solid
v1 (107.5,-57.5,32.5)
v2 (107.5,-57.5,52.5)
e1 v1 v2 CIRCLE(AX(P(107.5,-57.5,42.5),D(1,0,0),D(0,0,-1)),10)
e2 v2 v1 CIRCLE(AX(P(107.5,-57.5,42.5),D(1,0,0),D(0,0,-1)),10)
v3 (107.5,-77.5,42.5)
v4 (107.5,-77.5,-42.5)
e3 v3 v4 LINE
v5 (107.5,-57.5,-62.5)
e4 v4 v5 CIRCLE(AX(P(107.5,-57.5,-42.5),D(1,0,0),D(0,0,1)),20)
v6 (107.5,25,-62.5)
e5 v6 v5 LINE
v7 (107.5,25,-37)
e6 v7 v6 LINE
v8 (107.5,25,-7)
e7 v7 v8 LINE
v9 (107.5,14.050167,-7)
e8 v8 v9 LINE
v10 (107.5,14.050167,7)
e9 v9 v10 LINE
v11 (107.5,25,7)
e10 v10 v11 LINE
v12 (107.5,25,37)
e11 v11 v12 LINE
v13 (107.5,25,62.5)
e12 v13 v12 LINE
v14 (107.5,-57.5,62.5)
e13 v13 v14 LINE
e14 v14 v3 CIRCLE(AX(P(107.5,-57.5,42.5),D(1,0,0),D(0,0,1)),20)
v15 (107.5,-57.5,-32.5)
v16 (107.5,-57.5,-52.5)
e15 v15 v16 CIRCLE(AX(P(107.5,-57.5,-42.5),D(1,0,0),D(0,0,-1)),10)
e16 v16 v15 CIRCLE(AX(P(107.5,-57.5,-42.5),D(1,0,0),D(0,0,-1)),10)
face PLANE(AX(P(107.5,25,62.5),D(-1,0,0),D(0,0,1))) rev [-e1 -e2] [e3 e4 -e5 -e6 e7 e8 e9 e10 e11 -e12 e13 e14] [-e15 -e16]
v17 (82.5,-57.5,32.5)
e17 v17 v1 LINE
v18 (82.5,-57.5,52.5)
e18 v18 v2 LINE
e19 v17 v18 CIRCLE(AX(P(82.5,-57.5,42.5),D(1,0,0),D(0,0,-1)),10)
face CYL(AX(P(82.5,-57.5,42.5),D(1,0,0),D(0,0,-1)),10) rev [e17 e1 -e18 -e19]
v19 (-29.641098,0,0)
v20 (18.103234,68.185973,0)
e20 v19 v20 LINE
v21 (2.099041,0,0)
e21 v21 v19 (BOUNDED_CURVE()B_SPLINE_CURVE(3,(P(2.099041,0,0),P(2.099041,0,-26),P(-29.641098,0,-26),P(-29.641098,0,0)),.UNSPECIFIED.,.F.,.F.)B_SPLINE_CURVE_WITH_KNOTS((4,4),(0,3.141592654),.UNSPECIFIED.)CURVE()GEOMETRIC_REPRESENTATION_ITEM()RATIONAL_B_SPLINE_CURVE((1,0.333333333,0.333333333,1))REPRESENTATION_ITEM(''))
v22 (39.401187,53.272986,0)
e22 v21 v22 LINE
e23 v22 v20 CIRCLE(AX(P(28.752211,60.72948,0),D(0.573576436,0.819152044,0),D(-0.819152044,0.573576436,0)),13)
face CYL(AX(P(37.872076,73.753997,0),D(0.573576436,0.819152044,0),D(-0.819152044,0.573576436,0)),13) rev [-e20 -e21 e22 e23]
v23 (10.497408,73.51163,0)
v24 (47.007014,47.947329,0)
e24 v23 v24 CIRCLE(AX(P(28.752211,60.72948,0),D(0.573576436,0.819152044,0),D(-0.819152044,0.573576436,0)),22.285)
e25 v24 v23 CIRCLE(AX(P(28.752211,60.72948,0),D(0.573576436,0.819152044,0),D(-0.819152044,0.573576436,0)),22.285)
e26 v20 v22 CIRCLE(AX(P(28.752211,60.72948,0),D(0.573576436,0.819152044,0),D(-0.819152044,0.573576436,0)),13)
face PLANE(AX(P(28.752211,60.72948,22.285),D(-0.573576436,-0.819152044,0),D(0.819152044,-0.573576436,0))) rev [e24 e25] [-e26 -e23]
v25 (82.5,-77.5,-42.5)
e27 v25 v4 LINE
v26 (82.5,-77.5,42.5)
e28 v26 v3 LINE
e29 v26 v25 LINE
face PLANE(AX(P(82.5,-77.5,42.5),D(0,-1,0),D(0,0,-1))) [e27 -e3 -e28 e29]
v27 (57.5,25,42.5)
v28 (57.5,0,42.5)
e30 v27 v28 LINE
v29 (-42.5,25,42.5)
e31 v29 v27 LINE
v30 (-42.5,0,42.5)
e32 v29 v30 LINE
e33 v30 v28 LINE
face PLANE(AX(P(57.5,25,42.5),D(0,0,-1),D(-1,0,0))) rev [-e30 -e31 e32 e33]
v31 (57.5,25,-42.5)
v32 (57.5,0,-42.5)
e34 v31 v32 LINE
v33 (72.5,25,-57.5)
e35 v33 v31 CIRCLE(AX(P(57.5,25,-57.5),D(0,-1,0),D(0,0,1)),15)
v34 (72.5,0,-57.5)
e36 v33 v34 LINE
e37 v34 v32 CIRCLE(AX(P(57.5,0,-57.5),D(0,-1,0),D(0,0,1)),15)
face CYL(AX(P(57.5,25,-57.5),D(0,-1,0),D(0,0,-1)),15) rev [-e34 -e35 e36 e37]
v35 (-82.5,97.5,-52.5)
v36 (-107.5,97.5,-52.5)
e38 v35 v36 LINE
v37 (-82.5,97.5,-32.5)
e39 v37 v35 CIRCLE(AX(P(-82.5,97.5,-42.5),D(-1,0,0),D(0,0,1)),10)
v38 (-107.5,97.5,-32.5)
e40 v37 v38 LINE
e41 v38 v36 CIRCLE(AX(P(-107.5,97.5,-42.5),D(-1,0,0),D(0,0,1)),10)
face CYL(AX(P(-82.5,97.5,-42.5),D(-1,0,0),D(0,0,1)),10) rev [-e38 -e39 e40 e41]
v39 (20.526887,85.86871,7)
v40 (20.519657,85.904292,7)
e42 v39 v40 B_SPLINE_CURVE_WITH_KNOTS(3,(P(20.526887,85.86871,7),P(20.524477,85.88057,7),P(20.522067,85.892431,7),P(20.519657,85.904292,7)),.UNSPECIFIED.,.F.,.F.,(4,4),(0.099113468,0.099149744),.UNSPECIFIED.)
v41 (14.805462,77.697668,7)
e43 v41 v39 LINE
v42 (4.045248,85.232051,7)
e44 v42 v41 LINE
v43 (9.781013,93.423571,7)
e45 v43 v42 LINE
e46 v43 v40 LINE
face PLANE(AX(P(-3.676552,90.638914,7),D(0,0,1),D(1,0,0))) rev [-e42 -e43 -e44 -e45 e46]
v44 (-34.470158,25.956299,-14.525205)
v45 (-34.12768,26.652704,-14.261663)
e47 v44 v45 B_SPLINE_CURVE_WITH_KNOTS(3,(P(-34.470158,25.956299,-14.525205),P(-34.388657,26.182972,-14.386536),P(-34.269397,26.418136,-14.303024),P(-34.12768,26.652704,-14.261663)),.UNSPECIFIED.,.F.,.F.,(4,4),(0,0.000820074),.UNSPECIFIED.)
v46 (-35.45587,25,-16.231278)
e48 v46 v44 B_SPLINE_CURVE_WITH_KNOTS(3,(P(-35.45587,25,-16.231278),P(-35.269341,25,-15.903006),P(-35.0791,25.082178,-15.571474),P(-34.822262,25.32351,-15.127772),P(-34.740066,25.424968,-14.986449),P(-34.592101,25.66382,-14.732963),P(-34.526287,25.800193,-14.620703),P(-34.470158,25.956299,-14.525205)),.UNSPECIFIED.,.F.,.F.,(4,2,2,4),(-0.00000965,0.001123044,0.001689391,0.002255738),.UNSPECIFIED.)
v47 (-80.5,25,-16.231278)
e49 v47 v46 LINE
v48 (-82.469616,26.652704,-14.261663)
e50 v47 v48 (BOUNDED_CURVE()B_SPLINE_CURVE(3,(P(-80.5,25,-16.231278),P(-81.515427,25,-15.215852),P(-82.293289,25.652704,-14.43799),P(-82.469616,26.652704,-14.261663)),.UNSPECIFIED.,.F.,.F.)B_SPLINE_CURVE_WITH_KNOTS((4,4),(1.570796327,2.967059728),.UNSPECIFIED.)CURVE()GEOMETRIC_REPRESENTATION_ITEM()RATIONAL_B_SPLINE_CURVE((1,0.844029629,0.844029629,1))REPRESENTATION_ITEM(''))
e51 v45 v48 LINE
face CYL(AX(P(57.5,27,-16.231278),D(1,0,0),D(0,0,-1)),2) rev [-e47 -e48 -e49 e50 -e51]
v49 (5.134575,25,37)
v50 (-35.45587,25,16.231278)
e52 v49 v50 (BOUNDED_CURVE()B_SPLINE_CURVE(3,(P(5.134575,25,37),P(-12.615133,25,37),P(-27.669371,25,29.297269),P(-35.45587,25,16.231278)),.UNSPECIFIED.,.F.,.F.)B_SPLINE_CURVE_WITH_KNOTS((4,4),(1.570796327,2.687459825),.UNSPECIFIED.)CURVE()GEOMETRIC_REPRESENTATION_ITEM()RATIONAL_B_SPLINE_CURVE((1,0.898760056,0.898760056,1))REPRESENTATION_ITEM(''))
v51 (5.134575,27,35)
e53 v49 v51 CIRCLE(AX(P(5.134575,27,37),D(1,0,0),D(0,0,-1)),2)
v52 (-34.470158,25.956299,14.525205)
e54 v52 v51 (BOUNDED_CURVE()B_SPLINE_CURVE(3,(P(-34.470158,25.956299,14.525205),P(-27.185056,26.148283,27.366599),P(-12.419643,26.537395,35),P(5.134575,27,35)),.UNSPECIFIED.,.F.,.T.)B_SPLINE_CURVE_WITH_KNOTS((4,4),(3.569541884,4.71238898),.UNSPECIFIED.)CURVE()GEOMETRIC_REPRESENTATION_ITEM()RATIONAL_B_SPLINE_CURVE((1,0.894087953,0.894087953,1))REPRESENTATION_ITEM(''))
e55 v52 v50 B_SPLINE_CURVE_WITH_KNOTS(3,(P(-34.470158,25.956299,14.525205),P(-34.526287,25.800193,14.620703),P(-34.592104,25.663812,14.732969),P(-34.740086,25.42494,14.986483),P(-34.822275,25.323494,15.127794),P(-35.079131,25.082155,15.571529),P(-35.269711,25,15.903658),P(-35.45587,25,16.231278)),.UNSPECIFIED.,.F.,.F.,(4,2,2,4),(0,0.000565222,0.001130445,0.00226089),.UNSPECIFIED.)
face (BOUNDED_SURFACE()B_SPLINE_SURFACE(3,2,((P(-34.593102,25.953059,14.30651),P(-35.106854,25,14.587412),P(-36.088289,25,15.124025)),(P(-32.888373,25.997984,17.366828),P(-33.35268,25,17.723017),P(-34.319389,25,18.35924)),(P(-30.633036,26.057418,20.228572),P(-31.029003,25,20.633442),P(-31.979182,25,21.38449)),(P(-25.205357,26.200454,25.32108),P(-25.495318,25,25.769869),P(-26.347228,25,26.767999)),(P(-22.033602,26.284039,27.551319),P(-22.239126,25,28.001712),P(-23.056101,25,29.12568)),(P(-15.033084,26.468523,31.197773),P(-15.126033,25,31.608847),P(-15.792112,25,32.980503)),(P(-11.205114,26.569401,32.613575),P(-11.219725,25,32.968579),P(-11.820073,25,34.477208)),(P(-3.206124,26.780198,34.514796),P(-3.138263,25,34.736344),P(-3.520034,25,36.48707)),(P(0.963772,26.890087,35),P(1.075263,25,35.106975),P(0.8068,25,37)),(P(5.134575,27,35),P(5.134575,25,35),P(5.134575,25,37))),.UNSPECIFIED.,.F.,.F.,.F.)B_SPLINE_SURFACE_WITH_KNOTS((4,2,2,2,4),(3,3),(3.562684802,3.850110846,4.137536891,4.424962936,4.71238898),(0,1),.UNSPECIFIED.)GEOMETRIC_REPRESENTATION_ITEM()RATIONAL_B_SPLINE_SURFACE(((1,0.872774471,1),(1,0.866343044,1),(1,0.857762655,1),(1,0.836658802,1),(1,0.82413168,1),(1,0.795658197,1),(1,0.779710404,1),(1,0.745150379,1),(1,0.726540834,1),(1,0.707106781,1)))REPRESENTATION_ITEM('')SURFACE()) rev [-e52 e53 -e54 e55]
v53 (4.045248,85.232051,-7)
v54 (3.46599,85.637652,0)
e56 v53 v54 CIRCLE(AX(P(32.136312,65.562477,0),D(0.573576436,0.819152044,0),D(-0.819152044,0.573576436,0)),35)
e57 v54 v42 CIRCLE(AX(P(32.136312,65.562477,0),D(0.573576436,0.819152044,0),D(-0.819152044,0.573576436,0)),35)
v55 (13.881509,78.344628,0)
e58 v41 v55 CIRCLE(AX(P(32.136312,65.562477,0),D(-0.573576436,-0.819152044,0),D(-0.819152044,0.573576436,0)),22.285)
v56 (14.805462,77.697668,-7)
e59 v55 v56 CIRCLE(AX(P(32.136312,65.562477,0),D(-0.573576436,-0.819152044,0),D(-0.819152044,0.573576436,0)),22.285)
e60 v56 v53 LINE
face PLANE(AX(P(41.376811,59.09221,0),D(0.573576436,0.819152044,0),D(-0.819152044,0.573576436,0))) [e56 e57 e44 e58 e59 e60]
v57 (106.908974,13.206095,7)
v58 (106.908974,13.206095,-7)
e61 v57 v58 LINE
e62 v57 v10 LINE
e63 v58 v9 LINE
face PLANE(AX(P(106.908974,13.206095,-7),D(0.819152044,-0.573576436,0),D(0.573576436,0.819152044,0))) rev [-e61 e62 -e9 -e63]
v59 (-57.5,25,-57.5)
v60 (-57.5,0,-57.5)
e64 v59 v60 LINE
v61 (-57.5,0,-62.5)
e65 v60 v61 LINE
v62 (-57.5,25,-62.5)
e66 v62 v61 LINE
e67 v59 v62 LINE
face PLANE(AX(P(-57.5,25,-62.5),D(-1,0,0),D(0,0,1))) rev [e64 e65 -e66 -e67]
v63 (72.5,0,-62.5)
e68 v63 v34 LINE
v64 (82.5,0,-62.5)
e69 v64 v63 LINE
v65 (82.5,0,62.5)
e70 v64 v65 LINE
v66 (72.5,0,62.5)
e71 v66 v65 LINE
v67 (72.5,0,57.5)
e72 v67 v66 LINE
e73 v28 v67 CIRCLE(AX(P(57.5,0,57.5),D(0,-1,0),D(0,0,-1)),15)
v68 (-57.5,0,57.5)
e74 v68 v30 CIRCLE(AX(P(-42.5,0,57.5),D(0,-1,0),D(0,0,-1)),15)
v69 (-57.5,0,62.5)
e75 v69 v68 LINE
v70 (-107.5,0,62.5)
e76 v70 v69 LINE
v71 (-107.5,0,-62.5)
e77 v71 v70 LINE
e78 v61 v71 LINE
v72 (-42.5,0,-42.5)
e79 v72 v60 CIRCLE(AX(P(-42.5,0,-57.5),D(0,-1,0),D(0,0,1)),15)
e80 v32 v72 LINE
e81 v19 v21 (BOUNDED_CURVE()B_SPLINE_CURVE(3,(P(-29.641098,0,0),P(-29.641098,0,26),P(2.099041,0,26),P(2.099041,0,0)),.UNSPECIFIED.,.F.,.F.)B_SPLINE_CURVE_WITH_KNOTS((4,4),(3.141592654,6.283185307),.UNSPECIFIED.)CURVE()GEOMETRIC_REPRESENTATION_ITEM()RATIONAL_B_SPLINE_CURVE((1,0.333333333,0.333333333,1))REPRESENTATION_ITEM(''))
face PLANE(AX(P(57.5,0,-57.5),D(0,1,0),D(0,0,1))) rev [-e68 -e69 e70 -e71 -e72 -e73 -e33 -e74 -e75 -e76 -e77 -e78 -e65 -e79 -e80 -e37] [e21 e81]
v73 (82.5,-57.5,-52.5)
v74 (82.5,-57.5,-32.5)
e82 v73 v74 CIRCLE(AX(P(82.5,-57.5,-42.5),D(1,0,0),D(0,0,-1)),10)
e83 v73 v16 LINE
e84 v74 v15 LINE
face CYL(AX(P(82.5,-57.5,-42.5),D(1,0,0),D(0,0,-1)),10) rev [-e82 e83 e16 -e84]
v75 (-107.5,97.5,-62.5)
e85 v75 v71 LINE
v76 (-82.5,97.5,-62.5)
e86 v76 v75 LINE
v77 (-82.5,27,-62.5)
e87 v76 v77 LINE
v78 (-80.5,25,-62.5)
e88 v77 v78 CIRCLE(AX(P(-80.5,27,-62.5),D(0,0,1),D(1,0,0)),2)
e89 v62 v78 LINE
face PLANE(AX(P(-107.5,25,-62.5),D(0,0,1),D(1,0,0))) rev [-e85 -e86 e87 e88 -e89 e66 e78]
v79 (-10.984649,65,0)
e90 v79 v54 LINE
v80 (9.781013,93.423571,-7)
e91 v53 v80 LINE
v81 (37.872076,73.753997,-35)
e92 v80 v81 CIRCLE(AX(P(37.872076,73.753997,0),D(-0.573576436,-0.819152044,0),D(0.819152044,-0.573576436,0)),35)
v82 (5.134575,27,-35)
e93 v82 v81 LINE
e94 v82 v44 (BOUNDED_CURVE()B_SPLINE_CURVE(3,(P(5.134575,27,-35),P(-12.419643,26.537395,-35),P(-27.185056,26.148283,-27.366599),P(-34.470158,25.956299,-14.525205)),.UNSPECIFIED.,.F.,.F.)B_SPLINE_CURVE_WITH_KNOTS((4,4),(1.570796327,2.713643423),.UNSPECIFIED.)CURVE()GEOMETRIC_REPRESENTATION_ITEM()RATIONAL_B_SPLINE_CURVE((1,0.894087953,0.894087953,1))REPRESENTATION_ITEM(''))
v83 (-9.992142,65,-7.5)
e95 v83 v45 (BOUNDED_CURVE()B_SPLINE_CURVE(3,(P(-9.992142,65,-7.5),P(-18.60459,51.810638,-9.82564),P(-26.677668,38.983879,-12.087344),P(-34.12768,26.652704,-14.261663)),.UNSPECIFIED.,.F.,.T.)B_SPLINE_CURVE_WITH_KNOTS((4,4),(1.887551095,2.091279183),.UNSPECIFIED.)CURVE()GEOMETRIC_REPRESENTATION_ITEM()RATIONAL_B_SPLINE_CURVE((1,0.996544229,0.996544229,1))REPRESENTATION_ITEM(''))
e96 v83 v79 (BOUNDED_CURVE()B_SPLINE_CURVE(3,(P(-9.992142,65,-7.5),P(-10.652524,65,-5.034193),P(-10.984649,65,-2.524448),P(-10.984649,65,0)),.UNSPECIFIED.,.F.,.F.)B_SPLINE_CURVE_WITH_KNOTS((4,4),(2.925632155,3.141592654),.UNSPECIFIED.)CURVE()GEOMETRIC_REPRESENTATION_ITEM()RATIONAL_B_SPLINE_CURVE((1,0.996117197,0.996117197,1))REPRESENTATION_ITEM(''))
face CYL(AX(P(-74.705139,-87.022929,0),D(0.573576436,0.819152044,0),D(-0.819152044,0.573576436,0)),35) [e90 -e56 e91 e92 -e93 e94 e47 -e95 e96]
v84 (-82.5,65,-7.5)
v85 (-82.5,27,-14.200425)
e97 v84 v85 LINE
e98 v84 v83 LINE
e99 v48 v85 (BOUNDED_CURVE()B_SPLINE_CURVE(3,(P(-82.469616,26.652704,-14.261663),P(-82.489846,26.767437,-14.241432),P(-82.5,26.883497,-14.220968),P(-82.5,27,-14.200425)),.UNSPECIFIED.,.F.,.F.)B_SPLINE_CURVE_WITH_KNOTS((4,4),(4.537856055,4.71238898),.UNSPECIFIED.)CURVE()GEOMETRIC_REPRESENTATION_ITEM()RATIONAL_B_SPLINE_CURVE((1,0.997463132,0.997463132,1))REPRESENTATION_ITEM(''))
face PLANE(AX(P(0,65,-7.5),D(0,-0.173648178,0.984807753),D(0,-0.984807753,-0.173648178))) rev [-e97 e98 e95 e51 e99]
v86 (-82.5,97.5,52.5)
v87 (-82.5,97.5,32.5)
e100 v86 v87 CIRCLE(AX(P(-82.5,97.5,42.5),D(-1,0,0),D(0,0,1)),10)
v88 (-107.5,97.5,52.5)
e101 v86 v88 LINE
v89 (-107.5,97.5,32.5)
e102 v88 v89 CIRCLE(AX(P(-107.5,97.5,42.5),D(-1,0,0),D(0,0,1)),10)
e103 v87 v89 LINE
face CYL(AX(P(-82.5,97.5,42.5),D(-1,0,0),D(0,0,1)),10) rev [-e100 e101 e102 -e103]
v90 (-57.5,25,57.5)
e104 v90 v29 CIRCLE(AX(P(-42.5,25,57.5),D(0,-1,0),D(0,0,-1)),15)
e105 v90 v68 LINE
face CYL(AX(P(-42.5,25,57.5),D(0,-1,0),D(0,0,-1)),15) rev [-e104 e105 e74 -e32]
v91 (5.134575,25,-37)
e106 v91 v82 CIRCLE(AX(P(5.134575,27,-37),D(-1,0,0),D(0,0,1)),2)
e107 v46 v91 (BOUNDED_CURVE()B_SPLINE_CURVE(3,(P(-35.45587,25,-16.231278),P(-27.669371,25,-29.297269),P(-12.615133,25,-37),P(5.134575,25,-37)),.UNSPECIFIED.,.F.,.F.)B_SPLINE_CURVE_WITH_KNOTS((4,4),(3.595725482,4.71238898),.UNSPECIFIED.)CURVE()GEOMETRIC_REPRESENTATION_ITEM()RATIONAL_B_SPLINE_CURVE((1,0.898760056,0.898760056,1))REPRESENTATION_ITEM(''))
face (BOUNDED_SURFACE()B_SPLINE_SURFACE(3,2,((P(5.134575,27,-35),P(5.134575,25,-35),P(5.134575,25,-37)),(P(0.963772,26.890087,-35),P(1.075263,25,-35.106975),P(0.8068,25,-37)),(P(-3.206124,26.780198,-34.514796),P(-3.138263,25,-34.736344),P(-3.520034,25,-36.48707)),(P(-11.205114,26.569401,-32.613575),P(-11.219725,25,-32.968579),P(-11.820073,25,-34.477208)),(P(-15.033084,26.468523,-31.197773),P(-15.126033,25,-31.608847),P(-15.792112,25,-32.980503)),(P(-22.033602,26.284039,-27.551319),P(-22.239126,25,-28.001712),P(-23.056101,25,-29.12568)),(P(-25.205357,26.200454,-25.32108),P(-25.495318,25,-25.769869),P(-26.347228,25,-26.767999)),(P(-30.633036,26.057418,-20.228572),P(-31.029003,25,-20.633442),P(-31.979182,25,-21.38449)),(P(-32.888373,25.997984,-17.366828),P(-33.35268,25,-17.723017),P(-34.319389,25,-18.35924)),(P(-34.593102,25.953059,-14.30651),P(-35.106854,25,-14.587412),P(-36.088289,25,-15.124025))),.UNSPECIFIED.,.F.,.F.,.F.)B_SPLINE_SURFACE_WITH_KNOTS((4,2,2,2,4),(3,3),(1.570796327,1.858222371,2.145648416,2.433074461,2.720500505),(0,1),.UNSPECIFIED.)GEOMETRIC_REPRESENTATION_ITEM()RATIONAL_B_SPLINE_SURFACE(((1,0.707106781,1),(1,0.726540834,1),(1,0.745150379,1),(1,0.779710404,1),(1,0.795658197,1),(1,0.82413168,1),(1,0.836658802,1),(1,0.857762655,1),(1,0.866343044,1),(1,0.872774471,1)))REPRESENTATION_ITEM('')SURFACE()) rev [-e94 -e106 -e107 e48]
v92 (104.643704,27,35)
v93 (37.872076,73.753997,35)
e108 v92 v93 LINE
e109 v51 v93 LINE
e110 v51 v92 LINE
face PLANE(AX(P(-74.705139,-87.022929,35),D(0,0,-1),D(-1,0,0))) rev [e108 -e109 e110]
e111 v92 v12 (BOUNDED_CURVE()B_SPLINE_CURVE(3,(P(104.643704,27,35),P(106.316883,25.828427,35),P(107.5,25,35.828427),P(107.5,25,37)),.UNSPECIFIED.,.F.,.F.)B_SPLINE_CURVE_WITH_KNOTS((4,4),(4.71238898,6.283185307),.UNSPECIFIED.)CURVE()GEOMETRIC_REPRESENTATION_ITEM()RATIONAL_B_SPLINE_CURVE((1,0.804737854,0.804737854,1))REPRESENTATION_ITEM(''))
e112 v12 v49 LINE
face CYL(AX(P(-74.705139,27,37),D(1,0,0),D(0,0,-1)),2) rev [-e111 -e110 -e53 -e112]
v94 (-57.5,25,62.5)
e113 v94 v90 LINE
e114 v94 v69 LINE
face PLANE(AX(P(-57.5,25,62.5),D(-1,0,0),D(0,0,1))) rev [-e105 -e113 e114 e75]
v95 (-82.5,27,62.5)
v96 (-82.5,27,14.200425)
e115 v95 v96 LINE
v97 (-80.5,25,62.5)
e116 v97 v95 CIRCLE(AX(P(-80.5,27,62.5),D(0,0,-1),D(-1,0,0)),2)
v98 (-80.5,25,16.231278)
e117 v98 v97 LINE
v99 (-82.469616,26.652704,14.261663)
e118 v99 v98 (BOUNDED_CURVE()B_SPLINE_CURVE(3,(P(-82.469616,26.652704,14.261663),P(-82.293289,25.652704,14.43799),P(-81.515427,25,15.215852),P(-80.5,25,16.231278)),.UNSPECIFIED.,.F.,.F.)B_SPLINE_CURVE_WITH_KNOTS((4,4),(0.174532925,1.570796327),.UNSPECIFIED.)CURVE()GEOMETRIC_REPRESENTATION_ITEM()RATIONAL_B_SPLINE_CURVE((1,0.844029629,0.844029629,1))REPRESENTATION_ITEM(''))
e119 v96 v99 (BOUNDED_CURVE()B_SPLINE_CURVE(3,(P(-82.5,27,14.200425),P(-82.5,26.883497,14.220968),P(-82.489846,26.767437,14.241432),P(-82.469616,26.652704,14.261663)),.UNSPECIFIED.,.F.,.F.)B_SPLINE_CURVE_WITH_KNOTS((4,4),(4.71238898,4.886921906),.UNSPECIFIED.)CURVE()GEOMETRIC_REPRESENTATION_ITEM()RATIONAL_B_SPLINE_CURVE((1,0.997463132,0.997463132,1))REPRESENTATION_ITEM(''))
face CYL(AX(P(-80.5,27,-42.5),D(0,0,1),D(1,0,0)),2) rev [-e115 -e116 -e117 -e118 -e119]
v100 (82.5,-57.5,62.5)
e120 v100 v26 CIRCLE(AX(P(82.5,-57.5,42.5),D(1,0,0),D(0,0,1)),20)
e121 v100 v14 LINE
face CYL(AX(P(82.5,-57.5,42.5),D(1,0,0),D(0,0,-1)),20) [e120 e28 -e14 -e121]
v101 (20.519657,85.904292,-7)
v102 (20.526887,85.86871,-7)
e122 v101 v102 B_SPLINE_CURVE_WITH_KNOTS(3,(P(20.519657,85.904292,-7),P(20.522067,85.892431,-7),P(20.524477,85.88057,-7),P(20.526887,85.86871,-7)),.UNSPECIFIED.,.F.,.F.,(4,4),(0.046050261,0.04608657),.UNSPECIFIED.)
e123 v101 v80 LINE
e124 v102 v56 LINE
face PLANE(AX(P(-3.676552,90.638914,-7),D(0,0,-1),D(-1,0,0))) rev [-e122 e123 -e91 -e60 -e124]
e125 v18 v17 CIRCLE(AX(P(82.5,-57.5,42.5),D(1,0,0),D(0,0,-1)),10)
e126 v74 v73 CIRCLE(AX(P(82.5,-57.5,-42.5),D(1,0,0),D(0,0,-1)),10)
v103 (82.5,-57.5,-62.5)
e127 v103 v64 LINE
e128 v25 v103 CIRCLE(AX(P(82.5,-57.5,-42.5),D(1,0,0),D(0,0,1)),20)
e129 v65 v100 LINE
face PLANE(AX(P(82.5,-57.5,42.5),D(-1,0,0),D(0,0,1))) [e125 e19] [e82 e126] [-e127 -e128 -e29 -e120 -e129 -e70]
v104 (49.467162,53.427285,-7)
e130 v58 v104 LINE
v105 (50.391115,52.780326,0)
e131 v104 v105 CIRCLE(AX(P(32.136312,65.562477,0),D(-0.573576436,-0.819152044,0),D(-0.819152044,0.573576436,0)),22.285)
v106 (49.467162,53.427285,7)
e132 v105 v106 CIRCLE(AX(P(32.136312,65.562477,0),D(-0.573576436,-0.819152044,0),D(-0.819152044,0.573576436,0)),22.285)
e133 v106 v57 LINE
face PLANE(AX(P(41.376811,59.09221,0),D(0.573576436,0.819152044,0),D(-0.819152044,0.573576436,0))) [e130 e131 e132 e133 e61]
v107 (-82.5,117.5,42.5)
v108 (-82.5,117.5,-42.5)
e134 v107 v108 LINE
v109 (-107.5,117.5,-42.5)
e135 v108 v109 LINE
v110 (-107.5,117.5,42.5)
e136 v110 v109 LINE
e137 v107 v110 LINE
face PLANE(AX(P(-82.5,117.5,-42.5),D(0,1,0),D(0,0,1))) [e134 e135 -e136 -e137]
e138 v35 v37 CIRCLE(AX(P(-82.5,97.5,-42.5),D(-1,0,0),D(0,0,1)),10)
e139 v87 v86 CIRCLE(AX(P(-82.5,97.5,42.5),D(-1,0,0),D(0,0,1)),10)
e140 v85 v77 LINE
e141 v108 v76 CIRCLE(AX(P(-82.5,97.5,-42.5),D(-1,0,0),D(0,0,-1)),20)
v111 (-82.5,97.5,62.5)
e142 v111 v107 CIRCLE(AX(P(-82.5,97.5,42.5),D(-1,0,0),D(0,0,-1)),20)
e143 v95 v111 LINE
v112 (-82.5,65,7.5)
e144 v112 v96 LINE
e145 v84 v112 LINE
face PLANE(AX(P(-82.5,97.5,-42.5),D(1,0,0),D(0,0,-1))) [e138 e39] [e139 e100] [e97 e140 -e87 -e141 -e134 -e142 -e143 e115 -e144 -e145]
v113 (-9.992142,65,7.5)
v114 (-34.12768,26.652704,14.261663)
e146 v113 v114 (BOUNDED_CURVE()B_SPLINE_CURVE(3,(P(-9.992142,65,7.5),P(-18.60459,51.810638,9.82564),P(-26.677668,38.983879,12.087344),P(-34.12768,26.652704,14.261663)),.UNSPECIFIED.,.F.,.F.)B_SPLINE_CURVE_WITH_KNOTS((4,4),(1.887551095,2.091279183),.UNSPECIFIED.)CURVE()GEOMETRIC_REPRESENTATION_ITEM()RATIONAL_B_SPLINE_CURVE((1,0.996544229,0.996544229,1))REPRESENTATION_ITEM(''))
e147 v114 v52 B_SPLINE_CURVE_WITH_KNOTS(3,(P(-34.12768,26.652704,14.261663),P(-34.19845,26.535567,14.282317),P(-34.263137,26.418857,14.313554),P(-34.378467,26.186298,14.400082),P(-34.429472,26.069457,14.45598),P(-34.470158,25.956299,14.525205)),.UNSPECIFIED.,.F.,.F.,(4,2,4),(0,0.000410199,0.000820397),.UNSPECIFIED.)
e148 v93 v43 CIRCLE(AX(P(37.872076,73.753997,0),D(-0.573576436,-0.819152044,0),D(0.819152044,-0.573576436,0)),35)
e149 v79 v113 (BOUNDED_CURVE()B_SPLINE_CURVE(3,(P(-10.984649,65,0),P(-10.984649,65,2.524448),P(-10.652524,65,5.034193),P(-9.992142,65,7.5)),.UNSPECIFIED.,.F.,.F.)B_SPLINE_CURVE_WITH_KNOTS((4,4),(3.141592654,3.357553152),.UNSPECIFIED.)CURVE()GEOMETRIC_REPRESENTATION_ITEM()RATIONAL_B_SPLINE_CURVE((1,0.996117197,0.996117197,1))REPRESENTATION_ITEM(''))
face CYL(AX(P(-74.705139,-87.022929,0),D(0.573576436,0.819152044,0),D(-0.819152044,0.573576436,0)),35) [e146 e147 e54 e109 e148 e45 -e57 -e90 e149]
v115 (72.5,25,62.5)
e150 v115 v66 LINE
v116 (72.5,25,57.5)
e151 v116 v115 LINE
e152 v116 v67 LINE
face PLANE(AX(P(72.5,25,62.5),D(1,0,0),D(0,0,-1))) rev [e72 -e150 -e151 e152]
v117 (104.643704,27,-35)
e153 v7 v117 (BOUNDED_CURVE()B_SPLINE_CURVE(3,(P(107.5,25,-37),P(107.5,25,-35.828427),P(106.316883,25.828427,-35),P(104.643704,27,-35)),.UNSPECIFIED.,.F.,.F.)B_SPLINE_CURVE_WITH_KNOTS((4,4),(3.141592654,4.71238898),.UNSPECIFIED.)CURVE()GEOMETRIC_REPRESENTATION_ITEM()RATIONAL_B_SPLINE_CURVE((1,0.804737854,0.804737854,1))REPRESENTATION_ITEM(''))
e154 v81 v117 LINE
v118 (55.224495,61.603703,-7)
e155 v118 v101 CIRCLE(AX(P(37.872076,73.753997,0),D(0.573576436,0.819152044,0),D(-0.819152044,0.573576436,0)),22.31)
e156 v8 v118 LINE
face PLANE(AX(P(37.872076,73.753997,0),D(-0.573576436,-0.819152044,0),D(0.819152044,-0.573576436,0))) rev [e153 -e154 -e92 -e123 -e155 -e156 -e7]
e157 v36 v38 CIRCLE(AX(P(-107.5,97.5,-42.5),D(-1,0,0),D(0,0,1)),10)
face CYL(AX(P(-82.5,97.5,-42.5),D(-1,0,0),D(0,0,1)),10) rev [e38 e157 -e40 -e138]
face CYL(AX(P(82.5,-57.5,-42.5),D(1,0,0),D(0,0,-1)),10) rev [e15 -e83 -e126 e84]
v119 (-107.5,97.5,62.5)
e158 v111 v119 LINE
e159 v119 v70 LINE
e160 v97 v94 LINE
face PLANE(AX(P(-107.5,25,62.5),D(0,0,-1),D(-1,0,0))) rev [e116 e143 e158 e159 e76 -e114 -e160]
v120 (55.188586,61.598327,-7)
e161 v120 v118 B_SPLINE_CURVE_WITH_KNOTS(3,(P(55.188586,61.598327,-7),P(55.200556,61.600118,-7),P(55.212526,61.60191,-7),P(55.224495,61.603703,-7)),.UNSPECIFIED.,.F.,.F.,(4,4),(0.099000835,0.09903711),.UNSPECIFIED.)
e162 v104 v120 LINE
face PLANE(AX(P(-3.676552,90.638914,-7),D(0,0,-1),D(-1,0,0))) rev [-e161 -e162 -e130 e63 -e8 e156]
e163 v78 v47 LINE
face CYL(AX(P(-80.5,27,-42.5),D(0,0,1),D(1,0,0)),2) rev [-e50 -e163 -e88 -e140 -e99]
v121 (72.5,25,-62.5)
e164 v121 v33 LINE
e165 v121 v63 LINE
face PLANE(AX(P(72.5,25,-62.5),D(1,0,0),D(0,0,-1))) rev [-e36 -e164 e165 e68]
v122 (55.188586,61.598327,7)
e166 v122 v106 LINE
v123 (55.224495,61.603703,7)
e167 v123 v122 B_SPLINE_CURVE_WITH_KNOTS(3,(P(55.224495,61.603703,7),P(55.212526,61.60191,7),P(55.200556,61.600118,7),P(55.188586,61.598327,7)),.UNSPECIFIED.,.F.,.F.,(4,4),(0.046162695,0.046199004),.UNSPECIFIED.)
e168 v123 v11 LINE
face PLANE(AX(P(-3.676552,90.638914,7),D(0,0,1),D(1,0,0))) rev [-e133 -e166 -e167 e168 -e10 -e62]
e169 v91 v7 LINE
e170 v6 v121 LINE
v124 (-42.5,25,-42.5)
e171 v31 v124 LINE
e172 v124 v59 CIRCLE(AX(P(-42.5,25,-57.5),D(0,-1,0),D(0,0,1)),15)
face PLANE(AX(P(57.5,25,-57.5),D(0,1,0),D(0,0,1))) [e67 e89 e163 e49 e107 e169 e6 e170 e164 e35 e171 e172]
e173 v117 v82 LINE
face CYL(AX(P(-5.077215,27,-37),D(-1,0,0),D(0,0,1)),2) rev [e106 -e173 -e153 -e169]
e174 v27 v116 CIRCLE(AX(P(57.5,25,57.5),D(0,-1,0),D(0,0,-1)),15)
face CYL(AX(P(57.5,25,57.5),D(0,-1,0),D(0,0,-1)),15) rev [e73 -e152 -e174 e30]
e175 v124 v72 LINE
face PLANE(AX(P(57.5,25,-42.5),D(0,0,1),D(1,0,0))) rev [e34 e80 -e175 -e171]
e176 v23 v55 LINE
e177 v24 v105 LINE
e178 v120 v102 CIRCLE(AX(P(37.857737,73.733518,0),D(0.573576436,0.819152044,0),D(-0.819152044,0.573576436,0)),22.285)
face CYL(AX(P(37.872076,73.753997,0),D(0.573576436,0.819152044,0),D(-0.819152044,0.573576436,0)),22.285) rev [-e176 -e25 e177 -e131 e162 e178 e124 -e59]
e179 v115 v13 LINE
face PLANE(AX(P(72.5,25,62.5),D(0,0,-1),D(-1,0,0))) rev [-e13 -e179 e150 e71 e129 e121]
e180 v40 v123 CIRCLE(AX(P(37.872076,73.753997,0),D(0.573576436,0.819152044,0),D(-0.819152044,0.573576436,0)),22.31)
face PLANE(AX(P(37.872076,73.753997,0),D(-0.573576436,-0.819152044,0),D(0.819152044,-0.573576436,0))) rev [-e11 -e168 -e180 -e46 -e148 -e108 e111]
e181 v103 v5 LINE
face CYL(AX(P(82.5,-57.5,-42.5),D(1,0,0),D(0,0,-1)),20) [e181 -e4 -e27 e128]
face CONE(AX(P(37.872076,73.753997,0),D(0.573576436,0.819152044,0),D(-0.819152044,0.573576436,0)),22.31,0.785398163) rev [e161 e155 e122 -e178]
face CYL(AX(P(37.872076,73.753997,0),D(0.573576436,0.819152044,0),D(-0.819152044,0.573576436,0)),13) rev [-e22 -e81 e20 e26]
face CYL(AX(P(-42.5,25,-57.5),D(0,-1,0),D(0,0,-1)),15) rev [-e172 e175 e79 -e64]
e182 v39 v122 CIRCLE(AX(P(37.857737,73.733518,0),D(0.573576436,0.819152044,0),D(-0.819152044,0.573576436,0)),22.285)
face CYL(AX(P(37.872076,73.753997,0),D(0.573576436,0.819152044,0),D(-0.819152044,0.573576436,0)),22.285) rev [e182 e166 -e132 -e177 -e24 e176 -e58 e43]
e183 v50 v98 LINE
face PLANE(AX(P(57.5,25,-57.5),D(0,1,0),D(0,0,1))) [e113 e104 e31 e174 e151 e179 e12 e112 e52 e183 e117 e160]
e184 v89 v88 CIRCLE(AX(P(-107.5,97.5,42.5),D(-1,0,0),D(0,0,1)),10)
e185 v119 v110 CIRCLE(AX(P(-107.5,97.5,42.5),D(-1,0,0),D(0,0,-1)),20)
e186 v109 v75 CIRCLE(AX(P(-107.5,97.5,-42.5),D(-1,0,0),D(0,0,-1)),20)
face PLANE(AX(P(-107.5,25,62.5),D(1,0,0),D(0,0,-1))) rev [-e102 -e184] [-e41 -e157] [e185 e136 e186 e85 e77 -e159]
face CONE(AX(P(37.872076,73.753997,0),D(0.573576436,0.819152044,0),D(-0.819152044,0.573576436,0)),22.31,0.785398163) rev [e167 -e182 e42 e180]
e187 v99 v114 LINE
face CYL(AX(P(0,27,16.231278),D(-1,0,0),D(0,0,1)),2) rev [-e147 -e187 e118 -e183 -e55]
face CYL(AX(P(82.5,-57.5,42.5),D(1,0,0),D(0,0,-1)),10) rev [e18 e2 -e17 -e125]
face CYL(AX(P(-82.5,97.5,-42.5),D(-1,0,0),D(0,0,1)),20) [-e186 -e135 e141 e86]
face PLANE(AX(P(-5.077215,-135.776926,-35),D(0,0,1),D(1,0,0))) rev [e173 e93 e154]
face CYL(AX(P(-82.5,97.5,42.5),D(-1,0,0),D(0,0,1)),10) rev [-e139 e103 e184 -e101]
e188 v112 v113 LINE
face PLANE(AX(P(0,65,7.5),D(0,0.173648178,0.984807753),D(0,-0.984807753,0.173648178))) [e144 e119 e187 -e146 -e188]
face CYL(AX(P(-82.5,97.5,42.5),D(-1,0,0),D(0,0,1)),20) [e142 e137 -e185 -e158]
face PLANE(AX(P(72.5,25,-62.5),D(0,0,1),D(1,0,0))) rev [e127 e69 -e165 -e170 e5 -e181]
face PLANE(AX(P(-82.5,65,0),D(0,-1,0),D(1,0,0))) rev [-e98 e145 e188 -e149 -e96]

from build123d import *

# Parameters (mm, degrees)
BASE_PLATE_DEPTH             = 25
END_FLANGE_A_SKETCH_R        = 10
END_FLANGE_A_DEPTH           = 25
END_FLANGE_B_SKETCH_R        = 10
END_FLANGE_B_DEPTH           = 25
ANGLED_TRUNNION_BOSS_REACH   = 222.848
CLAMP_SLOT_SKETCH_W          = 135
CLAMP_SLOT_SKETCH_H          = 14
CLAMP_SLOT_14MM_DEPTH        = 10
SUPPORT_RIB_15MM_REACH       = 173.081
SUPPORT_RIB_SKETCH_WALL_W    = 415.677593096
SUPPORT_RIB_SKETCH_WALL_H    = 15
SUPPORT_RIB_15MM_DRAFT_ANGLE = 10
EDGE_FILLETS_R2_R            = 2


with BuildPart() as part:
    # Base Plate Sketch → Base Plate (new body)
    with BuildSketch(Plane(origin=(0, 0, 0), x_dir=(1, 0, 0), z_dir=(0, 1, 0))):
        with BuildLine():
            Line((72.5, 62.5), (107.5, 62.5))
            Line((107.5, 62.5), (107.5, -62.5))
            Line((107.5, -62.5), (72.5, -62.5))
            Line((72.5, -62.5), (72.5, -57.5))
            ThreePointArc((72.5, -57.5), (68.106601718, -46.893398282), (57.5, -42.5))
            Line((57.5, -42.5), (-42.5, -42.5))
            ThreePointArc((-42.5, -42.5), (-53.106601718, -46.893398282), (-57.5, -57.5))
            Line((-57.5, -57.5), (-57.5, -62.5))
            Line((-57.5, -62.5), (-107.5, -62.5))
            Line((-107.5, -62.5), (-107.5, 62.5))
            Line((-107.5, 62.5), (-57.5, 62.5))
            Line((-57.5, 62.5), (-57.5, 57.5))
            ThreePointArc((-57.5, 57.5), (-53.106601718, 46.893398282), (-42.5, 42.5))
            Line((-42.5, 42.5), (57.5, 42.5))
            ThreePointArc((57.5, 42.5), (68.106601718, 46.893398282), (72.5, 57.5))
            Line((72.5, 57.5), (72.5, 62.5))
        make_face()
    extrude(amount=BASE_PLATE_DEPTH)

    # End Flange A Sketch → End Flange A (add)
    with BuildSketch(Plane(origin=(107.5, 0, 0), x_dir=(0, 0, -1), z_dir=(1, 0, 0))):
        with BuildLine():
            Line((-62.5, 25), (62.5, 25))
            Line((62.5, 25), (62.5, -57.5))
            ThreePointArc((62.5, -57.5), (56.642135624, -71.642135624), (42.5, -77.5))
            Line((42.5, -77.5), (-42.5, -77.5))
            ThreePointArc((-42.5, -77.5), (-56.642135624, -71.642135624), (-62.5, -57.5))
            Line((-62.5, -57.5), (-62.5, 25))
        make_face()
        with Locations((-42.5, -57.5)):
            Circle(END_FLANGE_A_SKETCH_R, mode=Mode.SUBTRACT)
        with Locations((42.5, -57.5)):
            Circle(END_FLANGE_A_SKETCH_R, mode=Mode.SUBTRACT)
    extrude(amount=-END_FLANGE_A_DEPTH)

    # End Flange B Sketch → End Flange B (add)
    with BuildSketch(Plane.ZY.offset(107.5)):
        with BuildLine():
            Line((-62.5, 0), (62.5, 0))
            Line((62.5, 0), (62.5, 97.5))
            ThreePointArc((62.5, 97.5), (56.642135624, 111.642135624), (42.5, 117.5))
            Line((42.5, 117.5), (-42.5, 117.5))
            ThreePointArc((-42.5, 117.5), (-56.642135624, 111.642135624), (-62.5, 97.5))
            Line((-62.5, 97.5), (-62.5, 0))
        make_face()
        with Locations((-42.5, 97.5)):
            Circle(END_FLANGE_B_SKETCH_R, mode=Mode.SUBTRACT)
        with Locations((42.5, 97.5)):
            Circle(END_FLANGE_B_SKETCH_R, mode=Mode.SUBTRACT)
    extrude(amount=-END_FLANGE_B_DEPTH)

    # Angled Trunnion Boss: up to this face of the body (flat: up to its plane)
    angled_trunnion_boss_end = Plane(part.part.faces().sort_by_distance((13.835650778, 25, 0))[0])
    # Trunnion Boss Sketch → Angled Trunnion Boss (add, up to the picked face)
    with BuildSketch(Plane(origin=(47.112575056, 67.283730159, 0), x_dir=(0, 0, -1), z_dir=(-0.5735764363510502, -0.8191520442889889, 0)), mode=Mode.PRIVATE) as angled_trunnion_boss_sk1:
        with BuildLine():
            Line((-35, -11.280566148), (-35, 73.719433852))
            Line((-35, 73.719433852), (35, 73.719433852))
            Line((35, 73.719433852), (35, -11.280566148))
            ThreePointArc((35, -11.280566148), (0, -46.280566148), (-35, -11.280566148))
        make_face()
    angled_trunnion_boss_tool1 = split(extrude(angled_trunnion_boss_sk1.sketch, amount=ANGLED_TRUNNION_BOSS_REACH, mode=Mode.PRIVATE), bisect_by=angled_trunnion_boss_end, keep=Keep.BOTH, mode=Mode.PRIVATE)
    add(angled_trunnion_boss_tool1.solids().sort_by(Axis((61.205035, 57.416084, 0), (-0.5735764363510502, -0.8191520442889889, 0)))[0])

    # Sketch6 → Trunnion Bore CBORE M24 (revolve, cut)
    with BuildSketch(Plane(origin=(37.872076235, 73.75399709, 0), x_dir=(-0.8191520442889889, 0.5735764363510502, 0), z_dir=(0, 0, 1))):
        Polygon((0, 0), (0, 207.282018355), (13, 207.282018355), (13, 15.9), (22.285, 15.9), (22.285, 0.025), (22.31, 0), align=None)
    revolve(axis=Axis((41.514286606, 78.955612571, 0), (-0.5735764363510502, -0.8191520442889889, 0)), mode=Mode.SUBTRACT)

    # Clamp Slot Sketch → Clamp Slot 14mm (cut)
    with BuildSketch(Plane(origin=(47.112575056, 67.283730159, 0), x_dir=(0.819152044288989, -0.5735764363510502, 0), z_dir=(0.5735764363510502, 0.819152044288989, 0))):
        with Locations((12.5, 0)):
            Rectangle(CLAMP_SLOT_SKETCH_W, CLAMP_SLOT_SKETCH_H)
    extrude(amount=-CLAMP_SLOT_14MM_DEPTH, mode=Mode.SUBTRACT)

    # Support Rib Sketch wall → Support Rib 15mm (add, up to next)
    with BuildSketch(Plane(origin=(-46.742324561, 65, 0), x_dir=(1, 0, 0), z_dir=(0, 1, 0)), mode=Mode.PRIVATE) as support_rib_15mm_sk1:
        Rectangle(SUPPORT_RIB_SKETCH_WALL_W, SUPPORT_RIB_SKETCH_WALL_H)
    support_rib_15mm_tool1 = extrude(support_rib_15mm_sk1.sketch, amount=-SUPPORT_RIB_15MM_REACH, mode=Mode.PRIVATE) - part.part
    add(support_rib_15mm_tool1.solids().sort_by_distance((-46.742324561, 65, 0))[0])

    # Support Rib 15mm draft
    support_rib_15mm_draft_faces = [part.faces().sort_by_distance(p)[0] for p in [
        (-46.742324561, 64.5, -7.5),
        (-46.742324561, 64.5, 7.5),
    ]]
    draft(support_rib_15mm_draft_faces, Plane(origin=(-46.742324561, 65, 0), x_dir=(1, 0, 0), z_dir=(0, 1, 0)), SUPPORT_RIB_15MM_DRAFT_ANGLE)

    # Edge Fillets R2
    edge_fillets_r2_edges = [part.edges().sort_by_distance(p)[0] for p in [
        (55.617079978, 25, 35),
        (55.617079978, 25, -35),
        (-18.472856997, 25, -29.901342917),
        (-18.472856997, 25, 29.901342917),
        (-82.5, 25, -38.526539614),
        (-58.812113156, 25, -14.553079228),
        (-58.812113156, 25, 14.553079228),
        (-82.5, 25, 38.526539614),
    ]]
    fillet(edge_fillets_r2_edges, radius=EDGE_FILLETS_R2_R)


solid = part.part
